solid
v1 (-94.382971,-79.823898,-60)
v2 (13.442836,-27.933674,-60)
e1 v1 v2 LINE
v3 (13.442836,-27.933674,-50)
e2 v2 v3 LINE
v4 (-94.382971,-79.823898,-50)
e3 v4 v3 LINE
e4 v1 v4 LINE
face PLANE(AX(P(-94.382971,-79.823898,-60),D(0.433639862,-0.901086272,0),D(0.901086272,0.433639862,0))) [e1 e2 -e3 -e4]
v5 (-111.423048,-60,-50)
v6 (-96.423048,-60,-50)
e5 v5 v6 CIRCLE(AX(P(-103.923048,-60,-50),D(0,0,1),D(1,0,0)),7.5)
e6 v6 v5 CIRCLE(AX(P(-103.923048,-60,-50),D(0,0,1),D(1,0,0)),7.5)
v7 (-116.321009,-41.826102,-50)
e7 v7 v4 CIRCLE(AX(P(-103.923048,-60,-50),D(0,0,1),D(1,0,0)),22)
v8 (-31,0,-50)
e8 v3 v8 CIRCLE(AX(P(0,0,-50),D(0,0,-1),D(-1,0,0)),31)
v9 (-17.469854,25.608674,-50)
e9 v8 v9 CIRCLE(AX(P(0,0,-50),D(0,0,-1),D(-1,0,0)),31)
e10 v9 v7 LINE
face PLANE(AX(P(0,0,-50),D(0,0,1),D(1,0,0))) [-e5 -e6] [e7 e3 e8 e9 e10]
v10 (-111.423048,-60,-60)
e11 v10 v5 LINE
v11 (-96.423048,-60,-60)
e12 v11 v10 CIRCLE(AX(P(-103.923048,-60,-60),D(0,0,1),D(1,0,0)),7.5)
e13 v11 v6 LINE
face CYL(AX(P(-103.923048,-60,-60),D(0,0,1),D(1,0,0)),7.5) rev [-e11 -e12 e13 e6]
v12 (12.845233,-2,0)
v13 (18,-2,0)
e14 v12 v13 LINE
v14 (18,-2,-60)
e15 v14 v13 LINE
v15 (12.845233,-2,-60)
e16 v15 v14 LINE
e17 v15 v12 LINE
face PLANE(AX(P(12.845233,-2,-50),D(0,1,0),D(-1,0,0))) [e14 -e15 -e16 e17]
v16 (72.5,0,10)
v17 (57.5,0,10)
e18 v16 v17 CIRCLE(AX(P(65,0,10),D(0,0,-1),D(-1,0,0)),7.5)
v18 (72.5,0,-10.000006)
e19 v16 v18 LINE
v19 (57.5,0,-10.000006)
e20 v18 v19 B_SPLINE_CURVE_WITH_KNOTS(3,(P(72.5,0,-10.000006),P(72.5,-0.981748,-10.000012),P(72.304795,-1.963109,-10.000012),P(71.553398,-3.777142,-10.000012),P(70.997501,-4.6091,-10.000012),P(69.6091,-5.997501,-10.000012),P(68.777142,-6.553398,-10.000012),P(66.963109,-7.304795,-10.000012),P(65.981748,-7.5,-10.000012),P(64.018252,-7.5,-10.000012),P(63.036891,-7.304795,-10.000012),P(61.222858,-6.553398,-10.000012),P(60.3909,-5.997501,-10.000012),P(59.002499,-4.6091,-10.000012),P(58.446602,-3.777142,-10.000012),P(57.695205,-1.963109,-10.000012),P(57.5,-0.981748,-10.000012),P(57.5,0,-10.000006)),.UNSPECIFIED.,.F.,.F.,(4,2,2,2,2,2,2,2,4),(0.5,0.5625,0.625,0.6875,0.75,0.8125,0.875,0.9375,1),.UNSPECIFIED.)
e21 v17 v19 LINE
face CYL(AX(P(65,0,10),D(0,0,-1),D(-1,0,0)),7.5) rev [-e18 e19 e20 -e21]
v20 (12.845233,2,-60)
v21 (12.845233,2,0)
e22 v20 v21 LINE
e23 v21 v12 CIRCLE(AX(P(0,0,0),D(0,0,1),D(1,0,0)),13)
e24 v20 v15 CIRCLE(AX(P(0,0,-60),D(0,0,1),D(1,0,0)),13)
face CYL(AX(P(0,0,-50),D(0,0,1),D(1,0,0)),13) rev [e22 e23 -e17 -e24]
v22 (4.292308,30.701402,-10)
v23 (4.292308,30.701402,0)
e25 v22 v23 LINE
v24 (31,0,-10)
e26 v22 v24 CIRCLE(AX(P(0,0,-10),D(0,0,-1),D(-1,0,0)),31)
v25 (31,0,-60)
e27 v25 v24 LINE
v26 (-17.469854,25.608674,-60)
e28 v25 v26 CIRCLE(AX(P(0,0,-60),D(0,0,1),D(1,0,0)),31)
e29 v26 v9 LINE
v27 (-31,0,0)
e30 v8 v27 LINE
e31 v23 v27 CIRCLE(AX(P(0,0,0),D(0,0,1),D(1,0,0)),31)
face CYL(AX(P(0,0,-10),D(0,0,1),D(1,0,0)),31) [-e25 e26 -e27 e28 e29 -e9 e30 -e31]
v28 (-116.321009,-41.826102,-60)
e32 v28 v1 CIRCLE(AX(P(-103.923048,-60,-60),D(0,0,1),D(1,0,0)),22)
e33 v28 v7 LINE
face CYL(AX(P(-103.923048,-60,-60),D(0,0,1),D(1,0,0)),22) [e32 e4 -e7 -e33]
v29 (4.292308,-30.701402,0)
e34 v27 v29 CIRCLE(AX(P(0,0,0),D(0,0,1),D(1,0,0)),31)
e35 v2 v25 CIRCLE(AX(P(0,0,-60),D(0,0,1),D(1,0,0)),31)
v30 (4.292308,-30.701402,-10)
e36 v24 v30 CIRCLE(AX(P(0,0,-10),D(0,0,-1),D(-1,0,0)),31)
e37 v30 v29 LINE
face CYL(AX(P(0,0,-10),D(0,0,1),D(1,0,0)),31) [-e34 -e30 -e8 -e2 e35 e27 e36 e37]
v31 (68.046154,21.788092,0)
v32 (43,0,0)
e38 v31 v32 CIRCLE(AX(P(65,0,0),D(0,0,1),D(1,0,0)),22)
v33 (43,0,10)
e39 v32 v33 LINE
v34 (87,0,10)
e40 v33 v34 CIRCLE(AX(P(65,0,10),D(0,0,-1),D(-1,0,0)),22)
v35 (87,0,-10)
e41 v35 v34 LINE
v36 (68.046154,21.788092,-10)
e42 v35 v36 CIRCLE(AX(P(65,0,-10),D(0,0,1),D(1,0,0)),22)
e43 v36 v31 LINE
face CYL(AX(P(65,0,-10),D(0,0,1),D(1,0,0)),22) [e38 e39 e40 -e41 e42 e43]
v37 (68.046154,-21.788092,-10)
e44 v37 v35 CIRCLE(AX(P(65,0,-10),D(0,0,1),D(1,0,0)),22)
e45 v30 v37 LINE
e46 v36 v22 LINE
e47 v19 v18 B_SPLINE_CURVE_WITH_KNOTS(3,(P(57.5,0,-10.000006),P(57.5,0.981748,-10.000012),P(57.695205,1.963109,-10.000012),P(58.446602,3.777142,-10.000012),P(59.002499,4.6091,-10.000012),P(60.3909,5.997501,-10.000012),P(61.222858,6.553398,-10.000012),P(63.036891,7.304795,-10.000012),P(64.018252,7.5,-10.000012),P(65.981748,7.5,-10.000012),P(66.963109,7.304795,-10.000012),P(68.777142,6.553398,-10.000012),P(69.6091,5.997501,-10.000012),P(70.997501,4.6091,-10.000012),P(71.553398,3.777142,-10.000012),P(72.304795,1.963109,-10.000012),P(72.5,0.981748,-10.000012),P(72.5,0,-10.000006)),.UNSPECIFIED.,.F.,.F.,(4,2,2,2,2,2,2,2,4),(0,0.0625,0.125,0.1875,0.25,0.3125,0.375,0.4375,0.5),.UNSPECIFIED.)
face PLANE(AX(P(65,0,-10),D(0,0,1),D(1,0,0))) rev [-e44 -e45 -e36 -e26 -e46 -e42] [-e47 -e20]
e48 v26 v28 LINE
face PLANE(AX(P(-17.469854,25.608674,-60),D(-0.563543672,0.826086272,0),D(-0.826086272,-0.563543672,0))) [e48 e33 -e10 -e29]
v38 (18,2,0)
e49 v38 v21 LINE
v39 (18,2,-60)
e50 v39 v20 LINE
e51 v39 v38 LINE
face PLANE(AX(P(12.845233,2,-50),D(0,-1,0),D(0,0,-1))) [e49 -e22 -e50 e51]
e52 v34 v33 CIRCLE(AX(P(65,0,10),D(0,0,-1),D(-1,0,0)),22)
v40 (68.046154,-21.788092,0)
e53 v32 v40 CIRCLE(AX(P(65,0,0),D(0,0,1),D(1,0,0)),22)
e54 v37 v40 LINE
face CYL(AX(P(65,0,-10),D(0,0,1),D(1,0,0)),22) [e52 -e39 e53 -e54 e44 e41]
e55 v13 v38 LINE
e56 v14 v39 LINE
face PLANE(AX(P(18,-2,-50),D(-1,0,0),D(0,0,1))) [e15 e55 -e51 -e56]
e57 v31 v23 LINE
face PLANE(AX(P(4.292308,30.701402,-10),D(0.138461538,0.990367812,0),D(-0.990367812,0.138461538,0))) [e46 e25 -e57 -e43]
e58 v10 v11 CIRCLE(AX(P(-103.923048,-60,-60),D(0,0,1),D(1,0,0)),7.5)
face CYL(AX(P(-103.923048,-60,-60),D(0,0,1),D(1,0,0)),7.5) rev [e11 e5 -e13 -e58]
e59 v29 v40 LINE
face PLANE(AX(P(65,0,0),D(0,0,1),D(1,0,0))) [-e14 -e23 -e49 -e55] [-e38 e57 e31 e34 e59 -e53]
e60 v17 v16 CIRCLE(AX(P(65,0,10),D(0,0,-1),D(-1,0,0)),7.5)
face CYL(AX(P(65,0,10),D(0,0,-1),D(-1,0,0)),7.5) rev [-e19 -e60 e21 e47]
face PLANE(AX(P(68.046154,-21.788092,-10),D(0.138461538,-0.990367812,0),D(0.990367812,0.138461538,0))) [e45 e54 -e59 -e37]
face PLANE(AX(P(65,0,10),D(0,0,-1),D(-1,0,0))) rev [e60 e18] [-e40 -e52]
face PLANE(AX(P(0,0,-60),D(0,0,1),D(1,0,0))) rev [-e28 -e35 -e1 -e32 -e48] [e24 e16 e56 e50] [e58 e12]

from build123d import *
from build123d.topology import SkipClean

# Parameters (mm, degrees)
ARM_PLATE_DEPTH        = 10
HUB_START              = -20
HUB_BOSS_PROFILE_R     = 22
HUB_BOSS_PROFILE_R_2   = 7.5
HUB_BOSS_DEPTH         = 20
ARM_HOLE_DEPTH         = 95.498677239
ARM_HOLE_DEPTH_BACK    = 95.498677239
ARM_HOLE_PROFILE_R     = 7.5
HUB_HOUSING_PROFILE_R  = 31
HUB_HOUSING_DEPTH      = 40
KEYED_BORE_DEPTH       = 101.647901121
KEYED_BORE_DEPTH_BACK  = 101.647901121
ANGLED_ARM_PROFILE_R   = 7.5
ANGLED_ARM_PLATE_DEPTH = 10


with BuildPart() as part:
    # Arm Plate Profile → Arm Plate (new body)
    with BuildSketch(Plane.XY):
        with BuildLine():
            Line((4.292307692, 30.701402161), (68.046153846, 21.788091856))
            ThreePointArc((68.046153846, 21.788091856), (87, 0), (68.046153846, -21.788091856))
            Line((68.046153846, -21.788091856), (4.292307692, -30.701402161))
            ThreePointArc((4.292307692, -30.701402161), (-31, 0), (4.292307692, 30.701402161))
        make_face()
    extrude(amount=-ARM_PLATE_DEPTH)

    # Hub Boss Profile → Hub Boss (add)
    with SkipClean():  # the faces are left unmerged after this step: merging them gives an invalid solid
        with BuildSketch(Plane(origin=(0, 0, -10), x_dir=(-1, 0, 0), z_dir=(0, 0, -1)).offset(HUB_START)):
            with Locations(Location((-65, 0, 0), (0, 0, 262.041168118))):
                Circle(HUB_BOSS_PROFILE_R)
            with Locations((-65, 0)):
                Circle(HUB_BOSS_PROFILE_R_2, mode=Mode.SUBTRACT)
        extrude(amount=HUB_BOSS_DEPTH)

    # Arm Hole Profile → Arm Hole (cut, two sides: drawn at the far end of the back side and taken through both)
    with SkipClean():  # the faces are left unmerged after this step: merging them gives an invalid solid
        with BuildSketch(Plane(origin=(0, 0, -10), x_dir=(-1, 0, 0), z_dir=(0, 0, -1)).offset(-ARM_HOLE_DEPTH_BACK)):
            with Locations((-65, 0)):
                Circle(ARM_HOLE_PROFILE_R)
        extrude(amount=ARM_HOLE_DEPTH + ARM_HOLE_DEPTH_BACK, mode=Mode.SUBTRACT)

    # Hub Housing Profile → Hub Housing (add)
    with SkipClean():  # the faces are left unmerged after this step: merging them gives an invalid solid
        with BuildSketch(Plane(origin=(0, 0, -10), x_dir=(-1, 0, 0), z_dir=(0, 0, -1))):
            with Locations(Location((0, 0, 0), (0, 0, 97.958831882))):
                Circle(HUB_HOUSING_PROFILE_R)
            with BuildLine():
                Line((-12.845232579, -2), (-18, -2))
                Line((-18, -2), (-18, 2))
                Line((-18, 2), (-12.845232579, 2))
                ThreePointArc((-12.845232579, 2), (13, 0), (-12.845232579, -2))
            make_face(mode=Mode.SUBTRACT)
        extrude(amount=HUB_HOUSING_DEPTH)

    # Keyed Bore Profile → Keyed Bore (cut, two sides: drawn at the far end of the back side and taken through both)
    with SkipClean():  # the faces are left unmerged after this step: merging them gives an invalid solid
        with BuildSketch(Plane(origin=(0, 0, -10), x_dir=(-1, 0, 0), z_dir=(0, 0, -1)).offset(-KEYED_BORE_DEPTH_BACK)):
            with BuildLine():
                Line((-18, -2), (-12.845232579, -2))
                ThreePointArc((-12.845232579, -2), (13, 0), (-12.845232579, 2))
                Line((-12.845232579, 2), (-18, 2))
                Line((-18, 2), (-18, -2))
            make_face()
        extrude(amount=KEYED_BORE_DEPTH + KEYED_BORE_DEPTH_BACK, mode=Mode.SUBTRACT)

    # Angled Arm Profile → Angled Arm Plate (add)
    with SkipClean():  # the faces are left unmerged after this step: merging them gives an invalid solid
        with BuildSketch(Plane.XY.offset(-50)):
            with BuildLine():
                Line((-17.469853837, 25.608674447), (-116.321009242, -41.826102006))
                ThreePointArc((-116.321009242, -41.826102006), (-122.975607337, -71), (-94.382971499, -79.823897994))
                Line((-94.382971499, -79.823897994), (13.442835709, -27.933674447))
                ThreePointArc((13.442835709, -27.933674447), (26.846787517, 15.5), (-17.469853837, 25.608674447))
            make_face()
            with Locations((-103.923048454, -60)):
                Circle(ANGLED_ARM_PROFILE_R, mode=Mode.SUBTRACT)
            with BuildLine():
                Line((18, -2), (18, 2))
                Line((18, 2), (12.845232579, 2))
                ThreePointArc((12.845232579, 2), (-13, 0), (12.845232579, -2))
                Line((12.845232579, -2), (18, -2))
            make_face(mode=Mode.SUBTRACT)
        extrude(amount=-ANGLED_ARM_PLATE_DEPTH)


solid = part.part
